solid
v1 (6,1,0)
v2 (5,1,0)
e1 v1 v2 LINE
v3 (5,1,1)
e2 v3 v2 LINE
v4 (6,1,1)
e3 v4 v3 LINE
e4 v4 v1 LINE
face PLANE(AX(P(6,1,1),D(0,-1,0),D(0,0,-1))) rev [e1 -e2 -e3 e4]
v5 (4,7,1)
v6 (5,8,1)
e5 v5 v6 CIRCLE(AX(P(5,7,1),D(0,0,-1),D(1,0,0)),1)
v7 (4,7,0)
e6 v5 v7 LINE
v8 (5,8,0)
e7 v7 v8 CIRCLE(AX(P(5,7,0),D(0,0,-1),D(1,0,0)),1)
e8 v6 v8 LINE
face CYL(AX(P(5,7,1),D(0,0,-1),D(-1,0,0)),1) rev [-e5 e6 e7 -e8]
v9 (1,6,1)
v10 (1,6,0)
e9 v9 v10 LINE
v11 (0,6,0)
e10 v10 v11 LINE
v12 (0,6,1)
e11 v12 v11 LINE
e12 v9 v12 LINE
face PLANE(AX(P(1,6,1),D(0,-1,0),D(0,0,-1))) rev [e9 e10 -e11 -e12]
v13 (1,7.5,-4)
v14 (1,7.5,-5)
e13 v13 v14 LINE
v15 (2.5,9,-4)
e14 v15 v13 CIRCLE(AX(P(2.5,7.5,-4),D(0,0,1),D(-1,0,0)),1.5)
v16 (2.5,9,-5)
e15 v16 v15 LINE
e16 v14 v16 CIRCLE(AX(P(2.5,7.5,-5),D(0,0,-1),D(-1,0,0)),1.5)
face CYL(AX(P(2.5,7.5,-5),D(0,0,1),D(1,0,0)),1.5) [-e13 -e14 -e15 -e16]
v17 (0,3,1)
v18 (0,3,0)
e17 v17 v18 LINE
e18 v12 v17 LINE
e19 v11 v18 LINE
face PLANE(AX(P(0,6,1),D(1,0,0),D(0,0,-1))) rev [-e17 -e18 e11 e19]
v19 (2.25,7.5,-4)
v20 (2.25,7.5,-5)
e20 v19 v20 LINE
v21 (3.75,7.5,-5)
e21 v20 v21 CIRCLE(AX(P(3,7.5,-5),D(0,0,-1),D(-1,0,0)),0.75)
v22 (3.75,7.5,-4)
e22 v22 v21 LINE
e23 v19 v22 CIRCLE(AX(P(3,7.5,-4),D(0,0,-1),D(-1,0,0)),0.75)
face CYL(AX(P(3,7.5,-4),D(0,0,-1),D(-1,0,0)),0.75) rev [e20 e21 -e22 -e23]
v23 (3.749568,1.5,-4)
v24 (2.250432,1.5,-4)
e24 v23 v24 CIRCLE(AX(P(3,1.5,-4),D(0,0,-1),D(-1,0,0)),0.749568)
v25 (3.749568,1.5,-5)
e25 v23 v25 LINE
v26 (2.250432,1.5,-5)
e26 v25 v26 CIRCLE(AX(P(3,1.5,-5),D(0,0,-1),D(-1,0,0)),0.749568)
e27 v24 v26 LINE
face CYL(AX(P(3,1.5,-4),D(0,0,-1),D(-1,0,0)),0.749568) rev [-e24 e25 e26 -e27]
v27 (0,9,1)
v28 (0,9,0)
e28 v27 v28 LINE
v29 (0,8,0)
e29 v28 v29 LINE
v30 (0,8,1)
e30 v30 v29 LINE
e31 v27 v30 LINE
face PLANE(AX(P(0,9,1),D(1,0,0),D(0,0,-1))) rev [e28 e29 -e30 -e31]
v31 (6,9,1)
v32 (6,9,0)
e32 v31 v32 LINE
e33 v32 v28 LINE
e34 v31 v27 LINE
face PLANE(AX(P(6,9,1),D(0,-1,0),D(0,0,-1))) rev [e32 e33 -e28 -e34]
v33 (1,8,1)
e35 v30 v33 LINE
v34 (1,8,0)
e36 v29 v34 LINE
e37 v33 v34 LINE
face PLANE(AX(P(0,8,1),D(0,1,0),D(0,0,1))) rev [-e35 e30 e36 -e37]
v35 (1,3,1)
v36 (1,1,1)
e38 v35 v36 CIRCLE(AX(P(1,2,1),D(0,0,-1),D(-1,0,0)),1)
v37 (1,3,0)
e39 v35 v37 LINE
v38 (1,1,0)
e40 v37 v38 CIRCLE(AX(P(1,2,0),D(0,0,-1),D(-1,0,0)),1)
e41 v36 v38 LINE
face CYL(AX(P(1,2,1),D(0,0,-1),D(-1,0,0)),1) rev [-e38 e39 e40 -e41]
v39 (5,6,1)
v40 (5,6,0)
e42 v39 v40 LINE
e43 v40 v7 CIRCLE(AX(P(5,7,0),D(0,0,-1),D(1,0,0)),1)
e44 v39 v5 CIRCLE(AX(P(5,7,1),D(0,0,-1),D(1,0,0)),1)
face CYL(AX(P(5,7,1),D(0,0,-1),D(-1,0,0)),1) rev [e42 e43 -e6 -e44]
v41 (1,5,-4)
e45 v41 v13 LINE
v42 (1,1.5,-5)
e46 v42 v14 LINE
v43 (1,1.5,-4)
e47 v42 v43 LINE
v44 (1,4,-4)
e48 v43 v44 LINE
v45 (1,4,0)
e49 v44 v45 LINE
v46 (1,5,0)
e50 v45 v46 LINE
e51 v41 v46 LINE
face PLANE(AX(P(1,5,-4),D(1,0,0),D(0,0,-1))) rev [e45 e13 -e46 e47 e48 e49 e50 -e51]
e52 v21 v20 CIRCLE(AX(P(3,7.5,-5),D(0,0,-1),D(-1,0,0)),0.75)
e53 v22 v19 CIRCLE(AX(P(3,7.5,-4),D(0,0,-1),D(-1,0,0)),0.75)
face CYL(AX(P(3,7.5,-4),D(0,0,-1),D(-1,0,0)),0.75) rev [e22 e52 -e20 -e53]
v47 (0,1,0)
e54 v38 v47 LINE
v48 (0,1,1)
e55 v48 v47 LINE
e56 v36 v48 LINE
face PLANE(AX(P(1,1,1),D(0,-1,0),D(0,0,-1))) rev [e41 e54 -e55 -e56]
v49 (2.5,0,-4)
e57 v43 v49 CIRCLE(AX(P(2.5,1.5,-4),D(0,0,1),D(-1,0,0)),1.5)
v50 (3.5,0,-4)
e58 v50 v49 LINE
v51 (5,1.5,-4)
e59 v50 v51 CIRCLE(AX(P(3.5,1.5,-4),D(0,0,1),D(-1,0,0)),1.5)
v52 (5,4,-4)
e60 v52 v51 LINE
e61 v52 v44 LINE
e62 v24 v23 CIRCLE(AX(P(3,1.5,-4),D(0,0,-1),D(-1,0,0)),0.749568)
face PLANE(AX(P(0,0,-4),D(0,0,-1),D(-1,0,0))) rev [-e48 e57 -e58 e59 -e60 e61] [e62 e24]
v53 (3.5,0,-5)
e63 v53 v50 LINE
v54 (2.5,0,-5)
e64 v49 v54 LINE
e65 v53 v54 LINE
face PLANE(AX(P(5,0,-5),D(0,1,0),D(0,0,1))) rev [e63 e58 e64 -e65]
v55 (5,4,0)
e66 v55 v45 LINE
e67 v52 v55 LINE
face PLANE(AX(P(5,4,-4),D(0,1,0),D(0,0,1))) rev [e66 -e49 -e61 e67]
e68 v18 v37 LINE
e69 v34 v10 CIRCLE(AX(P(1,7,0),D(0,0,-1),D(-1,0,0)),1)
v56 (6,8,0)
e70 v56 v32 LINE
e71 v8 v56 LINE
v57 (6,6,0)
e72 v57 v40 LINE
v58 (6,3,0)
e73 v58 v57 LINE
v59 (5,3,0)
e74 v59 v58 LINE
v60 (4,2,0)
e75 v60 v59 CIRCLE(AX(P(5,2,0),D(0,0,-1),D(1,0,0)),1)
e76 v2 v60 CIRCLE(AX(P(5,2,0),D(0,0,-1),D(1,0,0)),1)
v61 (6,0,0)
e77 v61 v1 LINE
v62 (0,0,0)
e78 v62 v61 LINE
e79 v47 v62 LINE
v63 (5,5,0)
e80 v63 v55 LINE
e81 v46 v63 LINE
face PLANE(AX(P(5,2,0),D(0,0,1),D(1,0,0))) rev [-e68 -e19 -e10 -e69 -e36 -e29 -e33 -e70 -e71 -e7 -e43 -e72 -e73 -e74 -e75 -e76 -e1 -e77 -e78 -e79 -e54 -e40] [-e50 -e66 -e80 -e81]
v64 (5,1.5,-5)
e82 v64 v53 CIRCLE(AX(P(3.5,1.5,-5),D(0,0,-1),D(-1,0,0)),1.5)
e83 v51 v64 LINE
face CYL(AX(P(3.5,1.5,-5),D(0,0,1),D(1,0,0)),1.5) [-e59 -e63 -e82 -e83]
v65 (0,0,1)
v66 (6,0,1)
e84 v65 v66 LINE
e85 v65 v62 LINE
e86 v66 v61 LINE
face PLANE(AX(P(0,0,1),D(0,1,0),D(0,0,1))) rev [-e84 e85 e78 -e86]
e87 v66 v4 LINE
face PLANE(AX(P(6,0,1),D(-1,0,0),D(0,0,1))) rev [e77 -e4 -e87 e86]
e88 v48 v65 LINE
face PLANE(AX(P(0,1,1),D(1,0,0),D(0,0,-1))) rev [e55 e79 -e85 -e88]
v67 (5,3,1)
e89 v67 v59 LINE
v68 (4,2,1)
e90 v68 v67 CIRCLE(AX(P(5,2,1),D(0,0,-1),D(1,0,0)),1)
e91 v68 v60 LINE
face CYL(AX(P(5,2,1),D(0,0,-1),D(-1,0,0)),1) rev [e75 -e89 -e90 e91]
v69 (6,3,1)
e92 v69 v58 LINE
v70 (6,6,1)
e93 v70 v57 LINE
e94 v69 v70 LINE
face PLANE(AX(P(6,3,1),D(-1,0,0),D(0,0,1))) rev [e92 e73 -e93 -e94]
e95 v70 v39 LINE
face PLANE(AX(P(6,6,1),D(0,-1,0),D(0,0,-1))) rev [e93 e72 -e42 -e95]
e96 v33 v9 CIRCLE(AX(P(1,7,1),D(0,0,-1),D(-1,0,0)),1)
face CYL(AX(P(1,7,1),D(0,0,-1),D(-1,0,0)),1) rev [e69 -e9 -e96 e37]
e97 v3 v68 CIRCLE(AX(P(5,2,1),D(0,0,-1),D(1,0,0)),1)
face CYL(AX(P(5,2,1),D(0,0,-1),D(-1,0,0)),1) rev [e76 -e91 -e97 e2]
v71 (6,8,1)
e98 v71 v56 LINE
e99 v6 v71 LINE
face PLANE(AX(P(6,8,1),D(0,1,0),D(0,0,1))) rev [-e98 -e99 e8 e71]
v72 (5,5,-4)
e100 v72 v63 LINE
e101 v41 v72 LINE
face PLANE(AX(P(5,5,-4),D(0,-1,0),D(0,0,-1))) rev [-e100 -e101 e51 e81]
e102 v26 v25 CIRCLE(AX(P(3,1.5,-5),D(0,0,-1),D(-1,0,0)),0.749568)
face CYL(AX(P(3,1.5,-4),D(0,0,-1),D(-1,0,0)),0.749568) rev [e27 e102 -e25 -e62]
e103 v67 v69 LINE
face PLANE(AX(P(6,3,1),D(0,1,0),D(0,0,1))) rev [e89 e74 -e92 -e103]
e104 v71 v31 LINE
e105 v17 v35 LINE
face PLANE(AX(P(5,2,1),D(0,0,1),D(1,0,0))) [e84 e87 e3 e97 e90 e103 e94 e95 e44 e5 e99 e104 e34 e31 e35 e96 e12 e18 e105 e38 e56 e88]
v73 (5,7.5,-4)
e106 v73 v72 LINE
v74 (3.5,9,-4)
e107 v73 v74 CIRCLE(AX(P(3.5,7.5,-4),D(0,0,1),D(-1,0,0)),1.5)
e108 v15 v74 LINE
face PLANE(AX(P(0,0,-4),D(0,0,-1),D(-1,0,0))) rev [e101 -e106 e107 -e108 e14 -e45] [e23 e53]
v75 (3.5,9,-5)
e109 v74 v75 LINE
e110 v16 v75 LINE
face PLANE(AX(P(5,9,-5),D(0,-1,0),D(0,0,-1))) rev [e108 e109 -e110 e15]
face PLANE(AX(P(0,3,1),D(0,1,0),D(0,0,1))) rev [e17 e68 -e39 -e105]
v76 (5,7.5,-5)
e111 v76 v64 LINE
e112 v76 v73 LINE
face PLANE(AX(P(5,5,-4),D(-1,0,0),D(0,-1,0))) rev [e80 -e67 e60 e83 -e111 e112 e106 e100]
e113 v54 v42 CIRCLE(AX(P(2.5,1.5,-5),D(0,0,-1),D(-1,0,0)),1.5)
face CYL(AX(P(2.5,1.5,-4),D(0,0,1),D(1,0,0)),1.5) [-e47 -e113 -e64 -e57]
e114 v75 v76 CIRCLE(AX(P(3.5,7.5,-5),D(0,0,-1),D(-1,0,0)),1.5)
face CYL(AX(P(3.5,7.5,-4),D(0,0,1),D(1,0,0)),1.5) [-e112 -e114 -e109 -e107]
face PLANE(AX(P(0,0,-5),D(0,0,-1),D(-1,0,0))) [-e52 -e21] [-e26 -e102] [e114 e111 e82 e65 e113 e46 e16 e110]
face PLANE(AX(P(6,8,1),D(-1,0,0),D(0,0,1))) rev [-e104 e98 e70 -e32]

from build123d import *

# Parameters (mm, degrees)
BASE_PLATE_DEPTH         = 1
STANDOFF_WEB_SKETCH_W    = 4
STANDOFF_WEB_SKETCH_H    = 1
STANDOFF_WEB_4MM_DEPTH   = 4
FORK_LUG_SKETCH_W        = 4
FORK_LUG_SKETCH_H        = 9
FORK_LUG_DEPTH           = 1
LUG_END_FILLETS_R1_5_R   = 1.5
LUG_PIN_HOLES_SKETCH_R   = 0.75
LUG_PIN_HOLES_SKETCH_R_2 = 0.749568333
LUG_PIN_HOLES_DEPTH      = 1


with BuildPart() as part:
    # Base Plate Sketch → Base Plate (new body)
    with BuildSketch(Plane.XY):
        with BuildLine():
            Line((0, 0), (6, 0))
            Line((6, 0), (6, 1))
            Line((6, 1), (5, 1))
            ThreePointArc((5, 1), (4, 2), (5, 3))
            Line((5, 3), (6, 3))
            Line((6, 3), (6, 6))
            Line((6, 6), (5, 6))
            ThreePointArc((5, 6), (4, 7), (5, 8))
            Line((5, 8), (6, 8))
            Line((6, 8), (6, 9))
            Line((6, 9), (0, 9))
            Line((0, 9), (0, 8))
            Line((0, 8), (1, 8))
            ThreePointArc((1, 8), (2, 7), (1, 6))
            Line((1, 6), (0, 6))
            Line((0, 6), (0, 3))
            Line((0, 3), (1, 3))
            ThreePointArc((1, 3), (2, 2), (1, 1))
            Line((1, 1), (0, 1))
            Line((0, 1), (0, 0))
        make_face()
    extrude(amount=BASE_PLATE_DEPTH)

    # Standoff Web Sketch → Standoff Web 4mm (add)
    with BuildSketch(Plane(origin=(0, 0, 0), x_dir=(-1, 0, 0), z_dir=(0, 0, -1))):
        with Locations((-3, 4.5)):
            Rectangle(STANDOFF_WEB_SKETCH_W, STANDOFF_WEB_SKETCH_H)
    extrude(amount=STANDOFF_WEB_4MM_DEPTH)

    # Fork Lug Sketch → Fork Lug (add)
    with BuildSketch(Plane(origin=(0, 0, -4), x_dir=(-1, 0, 0), z_dir=(0, 0, -1))):
        with Locations((-3, 4.5)):
            Rectangle(FORK_LUG_SKETCH_W, FORK_LUG_SKETCH_H)
    extrude(amount=FORK_LUG_DEPTH)

    # Lug End Fillets R1.5
    lug_end_fillets_r1_5_edges = [part.edges().sort_by_distance(p)[0] for p in [
        (1, 0, -4.5),
        (1, 9, -4.5),
        (5, 9, -4.5),
        (5, 0, -4.5),
    ]]
    fillet(lug_end_fillets_r1_5_edges, radius=LUG_END_FILLETS_R1_5_R)

    # Lug Pin Holes Sketch → Lug Pin Holes (cut)
    with BuildSketch(Plane(origin=(0, 0, -5), x_dir=(-1, 0, 0), z_dir=(0, 0, -1))):
        with Locations((-3, 7.5)):
            Circle(LUG_PIN_HOLES_SKETCH_R)
        with Locations((-3, 1.5)):
            Circle(LUG_PIN_HOLES_SKETCH_R_2)
    extrude(amount=-LUG_PIN_HOLES_DEPTH, mode=Mode.SUBTRACT)


solid = part.part
